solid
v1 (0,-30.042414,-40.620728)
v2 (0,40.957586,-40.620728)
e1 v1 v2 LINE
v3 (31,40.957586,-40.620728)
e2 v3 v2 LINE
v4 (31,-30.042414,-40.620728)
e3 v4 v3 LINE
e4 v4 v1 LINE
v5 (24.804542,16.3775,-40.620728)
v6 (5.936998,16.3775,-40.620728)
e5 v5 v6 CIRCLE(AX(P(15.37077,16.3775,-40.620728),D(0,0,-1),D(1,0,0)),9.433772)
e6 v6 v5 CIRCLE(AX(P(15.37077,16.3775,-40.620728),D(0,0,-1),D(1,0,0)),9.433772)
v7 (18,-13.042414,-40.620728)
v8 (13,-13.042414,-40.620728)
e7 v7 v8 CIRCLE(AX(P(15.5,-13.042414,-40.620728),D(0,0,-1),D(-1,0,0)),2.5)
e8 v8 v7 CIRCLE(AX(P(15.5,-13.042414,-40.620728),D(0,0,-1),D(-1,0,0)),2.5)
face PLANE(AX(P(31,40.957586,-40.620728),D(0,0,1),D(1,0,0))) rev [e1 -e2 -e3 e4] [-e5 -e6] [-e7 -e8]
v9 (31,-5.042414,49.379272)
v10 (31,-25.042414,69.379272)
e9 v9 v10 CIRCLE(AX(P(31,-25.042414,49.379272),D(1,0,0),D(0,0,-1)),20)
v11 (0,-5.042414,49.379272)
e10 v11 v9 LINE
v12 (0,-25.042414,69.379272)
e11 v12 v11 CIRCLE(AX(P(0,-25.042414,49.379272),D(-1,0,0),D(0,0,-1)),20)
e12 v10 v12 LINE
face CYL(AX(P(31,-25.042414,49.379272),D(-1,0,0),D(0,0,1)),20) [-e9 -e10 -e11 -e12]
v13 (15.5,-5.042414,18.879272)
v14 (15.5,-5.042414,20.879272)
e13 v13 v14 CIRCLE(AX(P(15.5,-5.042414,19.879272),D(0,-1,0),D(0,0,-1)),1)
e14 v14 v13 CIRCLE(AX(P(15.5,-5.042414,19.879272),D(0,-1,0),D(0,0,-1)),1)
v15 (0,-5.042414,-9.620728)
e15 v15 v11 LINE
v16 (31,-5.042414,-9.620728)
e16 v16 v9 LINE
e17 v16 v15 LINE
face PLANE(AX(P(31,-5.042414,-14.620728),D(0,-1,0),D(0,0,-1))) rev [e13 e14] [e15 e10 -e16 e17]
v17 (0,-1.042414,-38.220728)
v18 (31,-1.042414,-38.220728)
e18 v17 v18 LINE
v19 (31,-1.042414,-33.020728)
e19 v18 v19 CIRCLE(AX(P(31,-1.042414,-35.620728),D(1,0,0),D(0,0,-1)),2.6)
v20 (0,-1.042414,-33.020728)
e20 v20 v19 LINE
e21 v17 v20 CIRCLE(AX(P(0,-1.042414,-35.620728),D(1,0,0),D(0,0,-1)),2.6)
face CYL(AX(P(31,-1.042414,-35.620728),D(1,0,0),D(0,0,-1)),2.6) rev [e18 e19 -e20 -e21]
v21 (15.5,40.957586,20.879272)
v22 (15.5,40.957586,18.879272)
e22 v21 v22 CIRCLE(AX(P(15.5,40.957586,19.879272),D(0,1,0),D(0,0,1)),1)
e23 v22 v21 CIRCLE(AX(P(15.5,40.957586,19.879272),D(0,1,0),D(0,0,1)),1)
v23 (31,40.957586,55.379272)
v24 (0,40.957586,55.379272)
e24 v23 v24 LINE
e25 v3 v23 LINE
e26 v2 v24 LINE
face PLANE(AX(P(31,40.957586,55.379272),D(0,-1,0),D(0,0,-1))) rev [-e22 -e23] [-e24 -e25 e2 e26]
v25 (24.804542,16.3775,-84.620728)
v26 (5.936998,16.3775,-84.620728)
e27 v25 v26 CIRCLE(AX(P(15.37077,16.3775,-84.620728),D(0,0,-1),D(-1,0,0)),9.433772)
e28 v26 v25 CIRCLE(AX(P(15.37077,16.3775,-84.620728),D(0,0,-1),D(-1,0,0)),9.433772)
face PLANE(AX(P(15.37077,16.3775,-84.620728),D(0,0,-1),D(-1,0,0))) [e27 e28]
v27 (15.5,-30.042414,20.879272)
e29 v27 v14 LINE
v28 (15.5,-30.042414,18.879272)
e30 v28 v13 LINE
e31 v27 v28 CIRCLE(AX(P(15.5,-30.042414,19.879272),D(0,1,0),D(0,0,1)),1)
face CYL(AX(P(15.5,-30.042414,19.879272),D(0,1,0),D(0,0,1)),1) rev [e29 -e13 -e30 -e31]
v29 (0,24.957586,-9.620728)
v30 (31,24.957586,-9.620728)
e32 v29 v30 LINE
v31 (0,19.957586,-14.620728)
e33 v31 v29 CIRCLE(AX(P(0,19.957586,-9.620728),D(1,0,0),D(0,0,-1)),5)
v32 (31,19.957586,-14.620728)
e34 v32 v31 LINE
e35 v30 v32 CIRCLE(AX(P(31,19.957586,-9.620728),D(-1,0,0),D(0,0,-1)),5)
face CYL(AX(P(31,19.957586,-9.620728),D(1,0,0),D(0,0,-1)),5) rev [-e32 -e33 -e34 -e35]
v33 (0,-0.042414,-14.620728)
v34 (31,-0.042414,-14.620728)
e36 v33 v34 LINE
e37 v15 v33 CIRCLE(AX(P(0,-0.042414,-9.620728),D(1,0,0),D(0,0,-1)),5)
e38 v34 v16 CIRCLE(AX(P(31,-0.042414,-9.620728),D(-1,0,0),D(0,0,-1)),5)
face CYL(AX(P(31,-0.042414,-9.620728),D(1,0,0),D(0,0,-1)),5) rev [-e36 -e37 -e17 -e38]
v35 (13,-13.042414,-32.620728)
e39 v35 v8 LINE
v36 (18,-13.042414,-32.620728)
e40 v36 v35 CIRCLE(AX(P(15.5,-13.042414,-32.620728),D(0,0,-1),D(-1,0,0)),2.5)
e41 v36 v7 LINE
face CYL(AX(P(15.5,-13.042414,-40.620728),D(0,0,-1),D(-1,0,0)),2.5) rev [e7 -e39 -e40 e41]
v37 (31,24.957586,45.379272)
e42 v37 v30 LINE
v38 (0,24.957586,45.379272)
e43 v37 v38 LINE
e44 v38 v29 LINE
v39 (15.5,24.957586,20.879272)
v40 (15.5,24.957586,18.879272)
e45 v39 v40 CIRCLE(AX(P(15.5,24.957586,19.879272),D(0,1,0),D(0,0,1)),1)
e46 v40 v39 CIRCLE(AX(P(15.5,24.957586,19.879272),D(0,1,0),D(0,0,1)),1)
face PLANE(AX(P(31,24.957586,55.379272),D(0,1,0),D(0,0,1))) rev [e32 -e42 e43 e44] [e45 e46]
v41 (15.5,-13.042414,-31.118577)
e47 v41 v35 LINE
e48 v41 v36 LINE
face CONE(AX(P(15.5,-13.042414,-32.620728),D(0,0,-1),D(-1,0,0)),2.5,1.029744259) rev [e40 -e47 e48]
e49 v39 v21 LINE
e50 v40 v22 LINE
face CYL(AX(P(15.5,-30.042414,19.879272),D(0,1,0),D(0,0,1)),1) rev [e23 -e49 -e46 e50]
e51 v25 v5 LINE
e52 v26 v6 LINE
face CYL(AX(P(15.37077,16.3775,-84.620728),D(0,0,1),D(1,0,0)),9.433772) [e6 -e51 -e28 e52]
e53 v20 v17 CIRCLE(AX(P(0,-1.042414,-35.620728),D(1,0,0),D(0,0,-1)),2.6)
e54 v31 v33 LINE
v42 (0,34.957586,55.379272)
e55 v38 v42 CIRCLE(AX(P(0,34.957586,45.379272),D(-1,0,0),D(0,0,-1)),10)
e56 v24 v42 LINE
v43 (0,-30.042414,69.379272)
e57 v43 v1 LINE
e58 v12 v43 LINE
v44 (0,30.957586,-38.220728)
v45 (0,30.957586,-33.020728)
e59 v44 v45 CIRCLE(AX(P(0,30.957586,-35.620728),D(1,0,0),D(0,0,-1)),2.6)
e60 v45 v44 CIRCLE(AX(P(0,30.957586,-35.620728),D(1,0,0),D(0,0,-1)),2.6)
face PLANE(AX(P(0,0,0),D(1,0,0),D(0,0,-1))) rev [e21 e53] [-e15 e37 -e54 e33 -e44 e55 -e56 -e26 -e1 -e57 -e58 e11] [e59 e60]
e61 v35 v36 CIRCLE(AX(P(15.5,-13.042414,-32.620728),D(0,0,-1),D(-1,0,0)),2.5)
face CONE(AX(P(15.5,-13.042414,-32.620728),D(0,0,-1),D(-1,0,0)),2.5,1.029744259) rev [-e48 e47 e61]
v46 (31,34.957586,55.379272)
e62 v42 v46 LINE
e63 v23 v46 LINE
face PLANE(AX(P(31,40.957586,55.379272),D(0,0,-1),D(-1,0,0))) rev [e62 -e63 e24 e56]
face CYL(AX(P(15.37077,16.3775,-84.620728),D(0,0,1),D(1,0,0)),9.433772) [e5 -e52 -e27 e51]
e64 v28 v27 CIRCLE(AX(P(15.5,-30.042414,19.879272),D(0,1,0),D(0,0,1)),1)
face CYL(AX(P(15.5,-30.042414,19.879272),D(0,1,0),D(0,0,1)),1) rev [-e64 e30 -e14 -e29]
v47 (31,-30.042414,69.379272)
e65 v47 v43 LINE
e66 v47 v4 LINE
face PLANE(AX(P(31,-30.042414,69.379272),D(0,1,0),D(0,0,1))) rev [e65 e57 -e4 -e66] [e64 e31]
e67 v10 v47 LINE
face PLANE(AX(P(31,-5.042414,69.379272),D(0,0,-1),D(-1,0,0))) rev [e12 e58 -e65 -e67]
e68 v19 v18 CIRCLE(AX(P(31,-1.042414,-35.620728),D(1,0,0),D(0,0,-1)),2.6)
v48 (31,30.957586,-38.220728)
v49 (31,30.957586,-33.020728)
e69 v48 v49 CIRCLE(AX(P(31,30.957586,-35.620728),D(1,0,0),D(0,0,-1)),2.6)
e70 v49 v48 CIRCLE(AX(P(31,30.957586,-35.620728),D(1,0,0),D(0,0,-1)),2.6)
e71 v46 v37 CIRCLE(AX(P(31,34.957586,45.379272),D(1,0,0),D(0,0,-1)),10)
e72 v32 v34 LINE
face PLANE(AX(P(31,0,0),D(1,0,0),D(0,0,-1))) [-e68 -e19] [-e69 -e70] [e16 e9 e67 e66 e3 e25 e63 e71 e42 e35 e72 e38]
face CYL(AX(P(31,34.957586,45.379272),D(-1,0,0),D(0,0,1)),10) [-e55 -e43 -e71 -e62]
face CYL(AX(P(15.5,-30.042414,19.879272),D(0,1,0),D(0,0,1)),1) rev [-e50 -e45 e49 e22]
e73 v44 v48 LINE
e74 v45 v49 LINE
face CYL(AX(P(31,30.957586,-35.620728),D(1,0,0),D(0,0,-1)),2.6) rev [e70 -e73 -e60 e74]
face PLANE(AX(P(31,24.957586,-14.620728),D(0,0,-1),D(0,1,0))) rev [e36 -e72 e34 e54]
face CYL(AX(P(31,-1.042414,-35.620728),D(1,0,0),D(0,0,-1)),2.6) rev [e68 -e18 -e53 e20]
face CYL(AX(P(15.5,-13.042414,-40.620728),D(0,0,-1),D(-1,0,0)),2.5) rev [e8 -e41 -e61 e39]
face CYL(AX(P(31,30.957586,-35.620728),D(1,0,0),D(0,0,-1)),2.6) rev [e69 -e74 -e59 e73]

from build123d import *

# Parameters (mm, degrees)
EXTRUDE_1_DEPTH             = 31
SKETCH_2_R                  = 1
CUT_EXTRUDE_1_DEPTH         = 104.997515993
FILLET_1_R                  = 10
FILLET_2_R                  = 20
FILLET_3_R                  = 5
HOLE_WIZARD_5_2_5_2_1_D     = 5.2
HOLE_WIZARD_5_2_5_2_1_DEPTH = 63
HOLE_WIZARD_5_2_5_2_1_TIP   = 1.562237609
HOLE_WIZARD_M6_1_D          = 5
HOLE_WIZARD_M6_1_DEPTH      = 8
HOLE_WIZARD_M6_1_TIP        = 1.502151548
SKETCH_7_R                  = 9.433771821
EXTRUDE_2_DEPTH             = 44


with BuildPart() as part:
    # 草图1 → 凸台-拉伸1 (new body)
    with BuildSketch(Plane(origin=(0, 0, 0), x_dir=(0, 0, -1), z_dir=(1, 0, 0))):
        Polygon((-55.379271635, 24.957586314), (14.620728365, 24.957586314), (14.620728365, -5.042413686), (-69.379271635, -5.042413686), (-69.379271635, -30.042413686), (40.620728365, -30.042413686), (40.620728365, 40.957586314), (-55.379271635, 40.957586314), align=None)
    extrude(amount=EXTRUDE_1_DEPTH)

    # 草图2 → 切除-拉伸1 (cut, through all)
    with BuildSketch(Plane(origin=(0, 40.957586314, 0), x_dir=(1, 0, 0), z_dir=(0, 1, 0))):
        with Locations(Location((15.5, -19.879271635, 0), (0, 0, 270))):
            Circle(SKETCH_2_R)
    extrude(amount=-CUT_EXTRUDE_1_DEPTH, mode=Mode.SUBTRACT)

    # 圆角1
    fillet_1_edges = [part.edges().sort_by_distance(p)[0] for p in [
        (15.5, 24.957586314, 55.379271635),
    ]]
    fillet(fillet_1_edges, radius=FILLET_1_R)

    # 圆角2
    fillet_2_edges = [part.edges().sort_by_distance(p)[0] for p in [
        (15.5, -5.042413686, 69.379271635),
    ]]
    fillet(fillet_2_edges, radius=FILLET_2_R)

    # 圆角3
    fillet_3_edges = [part.edges().sort_by_distance(p)[0] for p in [
        (15.5, -5.042413686, -14.620728365),
        (15.5, 24.957586314, -14.620728365),
    ]]
    fillet(fillet_3_edges, radius=FILLET_3_R)

    # Ø5.2 (5.2) 直径孔1
    with Locations(Plane(origin=(31, 0, 0), x_dir=(0, 0, -1), z_dir=(1, 0, 0))):
        with Locations((35.620728365, 30.957586314), (35.620728365, -1.042413686)):
            Hole(HOLE_WIZARD_5_2_5_2_1_D / 2, depth=HOLE_WIZARD_5_2_5_2_1_DEPTH)
            with Locations((0, 0, -(HOLE_WIZARD_5_2_5_2_1_DEPTH + HOLE_WIZARD_5_2_5_2_1_TIP / 2))):  # 118° drill point
                Cone(0, HOLE_WIZARD_5_2_5_2_1_D / 2, HOLE_WIZARD_5_2_5_2_1_TIP, mode=Mode.SUBTRACT)

    # M6 螺纹孔1
    with Locations(Plane(origin=(0, 0, -40.620728365), x_dir=(-1, 0, 0), z_dir=(0, 0, -1))):
        with Locations((-15.5, -13.042413686)):
            Hole(HOLE_WIZARD_M6_1_D / 2, depth=HOLE_WIZARD_M6_1_DEPTH)
            with Locations((0, 0, -(HOLE_WIZARD_M6_1_DEPTH + HOLE_WIZARD_M6_1_TIP / 2))):  # 118° drill point
                Cone(0, HOLE_WIZARD_M6_1_D / 2, HOLE_WIZARD_M6_1_TIP, mode=Mode.SUBTRACT)

    # 草图7 → 凸台-拉伸2 (add)
    with BuildSketch(Plane(origin=(0, 0, -40.620728365), x_dir=(-1, 0, 0), z_dir=(0, 0, -1))):
        with Locations(Location((-15.370770249, 16.377500271, 0), (0, 0, 180))):
            Circle(SKETCH_7_R)
    extrude(amount=EXTRUDE_2_DEPTH)


solid = part.part
